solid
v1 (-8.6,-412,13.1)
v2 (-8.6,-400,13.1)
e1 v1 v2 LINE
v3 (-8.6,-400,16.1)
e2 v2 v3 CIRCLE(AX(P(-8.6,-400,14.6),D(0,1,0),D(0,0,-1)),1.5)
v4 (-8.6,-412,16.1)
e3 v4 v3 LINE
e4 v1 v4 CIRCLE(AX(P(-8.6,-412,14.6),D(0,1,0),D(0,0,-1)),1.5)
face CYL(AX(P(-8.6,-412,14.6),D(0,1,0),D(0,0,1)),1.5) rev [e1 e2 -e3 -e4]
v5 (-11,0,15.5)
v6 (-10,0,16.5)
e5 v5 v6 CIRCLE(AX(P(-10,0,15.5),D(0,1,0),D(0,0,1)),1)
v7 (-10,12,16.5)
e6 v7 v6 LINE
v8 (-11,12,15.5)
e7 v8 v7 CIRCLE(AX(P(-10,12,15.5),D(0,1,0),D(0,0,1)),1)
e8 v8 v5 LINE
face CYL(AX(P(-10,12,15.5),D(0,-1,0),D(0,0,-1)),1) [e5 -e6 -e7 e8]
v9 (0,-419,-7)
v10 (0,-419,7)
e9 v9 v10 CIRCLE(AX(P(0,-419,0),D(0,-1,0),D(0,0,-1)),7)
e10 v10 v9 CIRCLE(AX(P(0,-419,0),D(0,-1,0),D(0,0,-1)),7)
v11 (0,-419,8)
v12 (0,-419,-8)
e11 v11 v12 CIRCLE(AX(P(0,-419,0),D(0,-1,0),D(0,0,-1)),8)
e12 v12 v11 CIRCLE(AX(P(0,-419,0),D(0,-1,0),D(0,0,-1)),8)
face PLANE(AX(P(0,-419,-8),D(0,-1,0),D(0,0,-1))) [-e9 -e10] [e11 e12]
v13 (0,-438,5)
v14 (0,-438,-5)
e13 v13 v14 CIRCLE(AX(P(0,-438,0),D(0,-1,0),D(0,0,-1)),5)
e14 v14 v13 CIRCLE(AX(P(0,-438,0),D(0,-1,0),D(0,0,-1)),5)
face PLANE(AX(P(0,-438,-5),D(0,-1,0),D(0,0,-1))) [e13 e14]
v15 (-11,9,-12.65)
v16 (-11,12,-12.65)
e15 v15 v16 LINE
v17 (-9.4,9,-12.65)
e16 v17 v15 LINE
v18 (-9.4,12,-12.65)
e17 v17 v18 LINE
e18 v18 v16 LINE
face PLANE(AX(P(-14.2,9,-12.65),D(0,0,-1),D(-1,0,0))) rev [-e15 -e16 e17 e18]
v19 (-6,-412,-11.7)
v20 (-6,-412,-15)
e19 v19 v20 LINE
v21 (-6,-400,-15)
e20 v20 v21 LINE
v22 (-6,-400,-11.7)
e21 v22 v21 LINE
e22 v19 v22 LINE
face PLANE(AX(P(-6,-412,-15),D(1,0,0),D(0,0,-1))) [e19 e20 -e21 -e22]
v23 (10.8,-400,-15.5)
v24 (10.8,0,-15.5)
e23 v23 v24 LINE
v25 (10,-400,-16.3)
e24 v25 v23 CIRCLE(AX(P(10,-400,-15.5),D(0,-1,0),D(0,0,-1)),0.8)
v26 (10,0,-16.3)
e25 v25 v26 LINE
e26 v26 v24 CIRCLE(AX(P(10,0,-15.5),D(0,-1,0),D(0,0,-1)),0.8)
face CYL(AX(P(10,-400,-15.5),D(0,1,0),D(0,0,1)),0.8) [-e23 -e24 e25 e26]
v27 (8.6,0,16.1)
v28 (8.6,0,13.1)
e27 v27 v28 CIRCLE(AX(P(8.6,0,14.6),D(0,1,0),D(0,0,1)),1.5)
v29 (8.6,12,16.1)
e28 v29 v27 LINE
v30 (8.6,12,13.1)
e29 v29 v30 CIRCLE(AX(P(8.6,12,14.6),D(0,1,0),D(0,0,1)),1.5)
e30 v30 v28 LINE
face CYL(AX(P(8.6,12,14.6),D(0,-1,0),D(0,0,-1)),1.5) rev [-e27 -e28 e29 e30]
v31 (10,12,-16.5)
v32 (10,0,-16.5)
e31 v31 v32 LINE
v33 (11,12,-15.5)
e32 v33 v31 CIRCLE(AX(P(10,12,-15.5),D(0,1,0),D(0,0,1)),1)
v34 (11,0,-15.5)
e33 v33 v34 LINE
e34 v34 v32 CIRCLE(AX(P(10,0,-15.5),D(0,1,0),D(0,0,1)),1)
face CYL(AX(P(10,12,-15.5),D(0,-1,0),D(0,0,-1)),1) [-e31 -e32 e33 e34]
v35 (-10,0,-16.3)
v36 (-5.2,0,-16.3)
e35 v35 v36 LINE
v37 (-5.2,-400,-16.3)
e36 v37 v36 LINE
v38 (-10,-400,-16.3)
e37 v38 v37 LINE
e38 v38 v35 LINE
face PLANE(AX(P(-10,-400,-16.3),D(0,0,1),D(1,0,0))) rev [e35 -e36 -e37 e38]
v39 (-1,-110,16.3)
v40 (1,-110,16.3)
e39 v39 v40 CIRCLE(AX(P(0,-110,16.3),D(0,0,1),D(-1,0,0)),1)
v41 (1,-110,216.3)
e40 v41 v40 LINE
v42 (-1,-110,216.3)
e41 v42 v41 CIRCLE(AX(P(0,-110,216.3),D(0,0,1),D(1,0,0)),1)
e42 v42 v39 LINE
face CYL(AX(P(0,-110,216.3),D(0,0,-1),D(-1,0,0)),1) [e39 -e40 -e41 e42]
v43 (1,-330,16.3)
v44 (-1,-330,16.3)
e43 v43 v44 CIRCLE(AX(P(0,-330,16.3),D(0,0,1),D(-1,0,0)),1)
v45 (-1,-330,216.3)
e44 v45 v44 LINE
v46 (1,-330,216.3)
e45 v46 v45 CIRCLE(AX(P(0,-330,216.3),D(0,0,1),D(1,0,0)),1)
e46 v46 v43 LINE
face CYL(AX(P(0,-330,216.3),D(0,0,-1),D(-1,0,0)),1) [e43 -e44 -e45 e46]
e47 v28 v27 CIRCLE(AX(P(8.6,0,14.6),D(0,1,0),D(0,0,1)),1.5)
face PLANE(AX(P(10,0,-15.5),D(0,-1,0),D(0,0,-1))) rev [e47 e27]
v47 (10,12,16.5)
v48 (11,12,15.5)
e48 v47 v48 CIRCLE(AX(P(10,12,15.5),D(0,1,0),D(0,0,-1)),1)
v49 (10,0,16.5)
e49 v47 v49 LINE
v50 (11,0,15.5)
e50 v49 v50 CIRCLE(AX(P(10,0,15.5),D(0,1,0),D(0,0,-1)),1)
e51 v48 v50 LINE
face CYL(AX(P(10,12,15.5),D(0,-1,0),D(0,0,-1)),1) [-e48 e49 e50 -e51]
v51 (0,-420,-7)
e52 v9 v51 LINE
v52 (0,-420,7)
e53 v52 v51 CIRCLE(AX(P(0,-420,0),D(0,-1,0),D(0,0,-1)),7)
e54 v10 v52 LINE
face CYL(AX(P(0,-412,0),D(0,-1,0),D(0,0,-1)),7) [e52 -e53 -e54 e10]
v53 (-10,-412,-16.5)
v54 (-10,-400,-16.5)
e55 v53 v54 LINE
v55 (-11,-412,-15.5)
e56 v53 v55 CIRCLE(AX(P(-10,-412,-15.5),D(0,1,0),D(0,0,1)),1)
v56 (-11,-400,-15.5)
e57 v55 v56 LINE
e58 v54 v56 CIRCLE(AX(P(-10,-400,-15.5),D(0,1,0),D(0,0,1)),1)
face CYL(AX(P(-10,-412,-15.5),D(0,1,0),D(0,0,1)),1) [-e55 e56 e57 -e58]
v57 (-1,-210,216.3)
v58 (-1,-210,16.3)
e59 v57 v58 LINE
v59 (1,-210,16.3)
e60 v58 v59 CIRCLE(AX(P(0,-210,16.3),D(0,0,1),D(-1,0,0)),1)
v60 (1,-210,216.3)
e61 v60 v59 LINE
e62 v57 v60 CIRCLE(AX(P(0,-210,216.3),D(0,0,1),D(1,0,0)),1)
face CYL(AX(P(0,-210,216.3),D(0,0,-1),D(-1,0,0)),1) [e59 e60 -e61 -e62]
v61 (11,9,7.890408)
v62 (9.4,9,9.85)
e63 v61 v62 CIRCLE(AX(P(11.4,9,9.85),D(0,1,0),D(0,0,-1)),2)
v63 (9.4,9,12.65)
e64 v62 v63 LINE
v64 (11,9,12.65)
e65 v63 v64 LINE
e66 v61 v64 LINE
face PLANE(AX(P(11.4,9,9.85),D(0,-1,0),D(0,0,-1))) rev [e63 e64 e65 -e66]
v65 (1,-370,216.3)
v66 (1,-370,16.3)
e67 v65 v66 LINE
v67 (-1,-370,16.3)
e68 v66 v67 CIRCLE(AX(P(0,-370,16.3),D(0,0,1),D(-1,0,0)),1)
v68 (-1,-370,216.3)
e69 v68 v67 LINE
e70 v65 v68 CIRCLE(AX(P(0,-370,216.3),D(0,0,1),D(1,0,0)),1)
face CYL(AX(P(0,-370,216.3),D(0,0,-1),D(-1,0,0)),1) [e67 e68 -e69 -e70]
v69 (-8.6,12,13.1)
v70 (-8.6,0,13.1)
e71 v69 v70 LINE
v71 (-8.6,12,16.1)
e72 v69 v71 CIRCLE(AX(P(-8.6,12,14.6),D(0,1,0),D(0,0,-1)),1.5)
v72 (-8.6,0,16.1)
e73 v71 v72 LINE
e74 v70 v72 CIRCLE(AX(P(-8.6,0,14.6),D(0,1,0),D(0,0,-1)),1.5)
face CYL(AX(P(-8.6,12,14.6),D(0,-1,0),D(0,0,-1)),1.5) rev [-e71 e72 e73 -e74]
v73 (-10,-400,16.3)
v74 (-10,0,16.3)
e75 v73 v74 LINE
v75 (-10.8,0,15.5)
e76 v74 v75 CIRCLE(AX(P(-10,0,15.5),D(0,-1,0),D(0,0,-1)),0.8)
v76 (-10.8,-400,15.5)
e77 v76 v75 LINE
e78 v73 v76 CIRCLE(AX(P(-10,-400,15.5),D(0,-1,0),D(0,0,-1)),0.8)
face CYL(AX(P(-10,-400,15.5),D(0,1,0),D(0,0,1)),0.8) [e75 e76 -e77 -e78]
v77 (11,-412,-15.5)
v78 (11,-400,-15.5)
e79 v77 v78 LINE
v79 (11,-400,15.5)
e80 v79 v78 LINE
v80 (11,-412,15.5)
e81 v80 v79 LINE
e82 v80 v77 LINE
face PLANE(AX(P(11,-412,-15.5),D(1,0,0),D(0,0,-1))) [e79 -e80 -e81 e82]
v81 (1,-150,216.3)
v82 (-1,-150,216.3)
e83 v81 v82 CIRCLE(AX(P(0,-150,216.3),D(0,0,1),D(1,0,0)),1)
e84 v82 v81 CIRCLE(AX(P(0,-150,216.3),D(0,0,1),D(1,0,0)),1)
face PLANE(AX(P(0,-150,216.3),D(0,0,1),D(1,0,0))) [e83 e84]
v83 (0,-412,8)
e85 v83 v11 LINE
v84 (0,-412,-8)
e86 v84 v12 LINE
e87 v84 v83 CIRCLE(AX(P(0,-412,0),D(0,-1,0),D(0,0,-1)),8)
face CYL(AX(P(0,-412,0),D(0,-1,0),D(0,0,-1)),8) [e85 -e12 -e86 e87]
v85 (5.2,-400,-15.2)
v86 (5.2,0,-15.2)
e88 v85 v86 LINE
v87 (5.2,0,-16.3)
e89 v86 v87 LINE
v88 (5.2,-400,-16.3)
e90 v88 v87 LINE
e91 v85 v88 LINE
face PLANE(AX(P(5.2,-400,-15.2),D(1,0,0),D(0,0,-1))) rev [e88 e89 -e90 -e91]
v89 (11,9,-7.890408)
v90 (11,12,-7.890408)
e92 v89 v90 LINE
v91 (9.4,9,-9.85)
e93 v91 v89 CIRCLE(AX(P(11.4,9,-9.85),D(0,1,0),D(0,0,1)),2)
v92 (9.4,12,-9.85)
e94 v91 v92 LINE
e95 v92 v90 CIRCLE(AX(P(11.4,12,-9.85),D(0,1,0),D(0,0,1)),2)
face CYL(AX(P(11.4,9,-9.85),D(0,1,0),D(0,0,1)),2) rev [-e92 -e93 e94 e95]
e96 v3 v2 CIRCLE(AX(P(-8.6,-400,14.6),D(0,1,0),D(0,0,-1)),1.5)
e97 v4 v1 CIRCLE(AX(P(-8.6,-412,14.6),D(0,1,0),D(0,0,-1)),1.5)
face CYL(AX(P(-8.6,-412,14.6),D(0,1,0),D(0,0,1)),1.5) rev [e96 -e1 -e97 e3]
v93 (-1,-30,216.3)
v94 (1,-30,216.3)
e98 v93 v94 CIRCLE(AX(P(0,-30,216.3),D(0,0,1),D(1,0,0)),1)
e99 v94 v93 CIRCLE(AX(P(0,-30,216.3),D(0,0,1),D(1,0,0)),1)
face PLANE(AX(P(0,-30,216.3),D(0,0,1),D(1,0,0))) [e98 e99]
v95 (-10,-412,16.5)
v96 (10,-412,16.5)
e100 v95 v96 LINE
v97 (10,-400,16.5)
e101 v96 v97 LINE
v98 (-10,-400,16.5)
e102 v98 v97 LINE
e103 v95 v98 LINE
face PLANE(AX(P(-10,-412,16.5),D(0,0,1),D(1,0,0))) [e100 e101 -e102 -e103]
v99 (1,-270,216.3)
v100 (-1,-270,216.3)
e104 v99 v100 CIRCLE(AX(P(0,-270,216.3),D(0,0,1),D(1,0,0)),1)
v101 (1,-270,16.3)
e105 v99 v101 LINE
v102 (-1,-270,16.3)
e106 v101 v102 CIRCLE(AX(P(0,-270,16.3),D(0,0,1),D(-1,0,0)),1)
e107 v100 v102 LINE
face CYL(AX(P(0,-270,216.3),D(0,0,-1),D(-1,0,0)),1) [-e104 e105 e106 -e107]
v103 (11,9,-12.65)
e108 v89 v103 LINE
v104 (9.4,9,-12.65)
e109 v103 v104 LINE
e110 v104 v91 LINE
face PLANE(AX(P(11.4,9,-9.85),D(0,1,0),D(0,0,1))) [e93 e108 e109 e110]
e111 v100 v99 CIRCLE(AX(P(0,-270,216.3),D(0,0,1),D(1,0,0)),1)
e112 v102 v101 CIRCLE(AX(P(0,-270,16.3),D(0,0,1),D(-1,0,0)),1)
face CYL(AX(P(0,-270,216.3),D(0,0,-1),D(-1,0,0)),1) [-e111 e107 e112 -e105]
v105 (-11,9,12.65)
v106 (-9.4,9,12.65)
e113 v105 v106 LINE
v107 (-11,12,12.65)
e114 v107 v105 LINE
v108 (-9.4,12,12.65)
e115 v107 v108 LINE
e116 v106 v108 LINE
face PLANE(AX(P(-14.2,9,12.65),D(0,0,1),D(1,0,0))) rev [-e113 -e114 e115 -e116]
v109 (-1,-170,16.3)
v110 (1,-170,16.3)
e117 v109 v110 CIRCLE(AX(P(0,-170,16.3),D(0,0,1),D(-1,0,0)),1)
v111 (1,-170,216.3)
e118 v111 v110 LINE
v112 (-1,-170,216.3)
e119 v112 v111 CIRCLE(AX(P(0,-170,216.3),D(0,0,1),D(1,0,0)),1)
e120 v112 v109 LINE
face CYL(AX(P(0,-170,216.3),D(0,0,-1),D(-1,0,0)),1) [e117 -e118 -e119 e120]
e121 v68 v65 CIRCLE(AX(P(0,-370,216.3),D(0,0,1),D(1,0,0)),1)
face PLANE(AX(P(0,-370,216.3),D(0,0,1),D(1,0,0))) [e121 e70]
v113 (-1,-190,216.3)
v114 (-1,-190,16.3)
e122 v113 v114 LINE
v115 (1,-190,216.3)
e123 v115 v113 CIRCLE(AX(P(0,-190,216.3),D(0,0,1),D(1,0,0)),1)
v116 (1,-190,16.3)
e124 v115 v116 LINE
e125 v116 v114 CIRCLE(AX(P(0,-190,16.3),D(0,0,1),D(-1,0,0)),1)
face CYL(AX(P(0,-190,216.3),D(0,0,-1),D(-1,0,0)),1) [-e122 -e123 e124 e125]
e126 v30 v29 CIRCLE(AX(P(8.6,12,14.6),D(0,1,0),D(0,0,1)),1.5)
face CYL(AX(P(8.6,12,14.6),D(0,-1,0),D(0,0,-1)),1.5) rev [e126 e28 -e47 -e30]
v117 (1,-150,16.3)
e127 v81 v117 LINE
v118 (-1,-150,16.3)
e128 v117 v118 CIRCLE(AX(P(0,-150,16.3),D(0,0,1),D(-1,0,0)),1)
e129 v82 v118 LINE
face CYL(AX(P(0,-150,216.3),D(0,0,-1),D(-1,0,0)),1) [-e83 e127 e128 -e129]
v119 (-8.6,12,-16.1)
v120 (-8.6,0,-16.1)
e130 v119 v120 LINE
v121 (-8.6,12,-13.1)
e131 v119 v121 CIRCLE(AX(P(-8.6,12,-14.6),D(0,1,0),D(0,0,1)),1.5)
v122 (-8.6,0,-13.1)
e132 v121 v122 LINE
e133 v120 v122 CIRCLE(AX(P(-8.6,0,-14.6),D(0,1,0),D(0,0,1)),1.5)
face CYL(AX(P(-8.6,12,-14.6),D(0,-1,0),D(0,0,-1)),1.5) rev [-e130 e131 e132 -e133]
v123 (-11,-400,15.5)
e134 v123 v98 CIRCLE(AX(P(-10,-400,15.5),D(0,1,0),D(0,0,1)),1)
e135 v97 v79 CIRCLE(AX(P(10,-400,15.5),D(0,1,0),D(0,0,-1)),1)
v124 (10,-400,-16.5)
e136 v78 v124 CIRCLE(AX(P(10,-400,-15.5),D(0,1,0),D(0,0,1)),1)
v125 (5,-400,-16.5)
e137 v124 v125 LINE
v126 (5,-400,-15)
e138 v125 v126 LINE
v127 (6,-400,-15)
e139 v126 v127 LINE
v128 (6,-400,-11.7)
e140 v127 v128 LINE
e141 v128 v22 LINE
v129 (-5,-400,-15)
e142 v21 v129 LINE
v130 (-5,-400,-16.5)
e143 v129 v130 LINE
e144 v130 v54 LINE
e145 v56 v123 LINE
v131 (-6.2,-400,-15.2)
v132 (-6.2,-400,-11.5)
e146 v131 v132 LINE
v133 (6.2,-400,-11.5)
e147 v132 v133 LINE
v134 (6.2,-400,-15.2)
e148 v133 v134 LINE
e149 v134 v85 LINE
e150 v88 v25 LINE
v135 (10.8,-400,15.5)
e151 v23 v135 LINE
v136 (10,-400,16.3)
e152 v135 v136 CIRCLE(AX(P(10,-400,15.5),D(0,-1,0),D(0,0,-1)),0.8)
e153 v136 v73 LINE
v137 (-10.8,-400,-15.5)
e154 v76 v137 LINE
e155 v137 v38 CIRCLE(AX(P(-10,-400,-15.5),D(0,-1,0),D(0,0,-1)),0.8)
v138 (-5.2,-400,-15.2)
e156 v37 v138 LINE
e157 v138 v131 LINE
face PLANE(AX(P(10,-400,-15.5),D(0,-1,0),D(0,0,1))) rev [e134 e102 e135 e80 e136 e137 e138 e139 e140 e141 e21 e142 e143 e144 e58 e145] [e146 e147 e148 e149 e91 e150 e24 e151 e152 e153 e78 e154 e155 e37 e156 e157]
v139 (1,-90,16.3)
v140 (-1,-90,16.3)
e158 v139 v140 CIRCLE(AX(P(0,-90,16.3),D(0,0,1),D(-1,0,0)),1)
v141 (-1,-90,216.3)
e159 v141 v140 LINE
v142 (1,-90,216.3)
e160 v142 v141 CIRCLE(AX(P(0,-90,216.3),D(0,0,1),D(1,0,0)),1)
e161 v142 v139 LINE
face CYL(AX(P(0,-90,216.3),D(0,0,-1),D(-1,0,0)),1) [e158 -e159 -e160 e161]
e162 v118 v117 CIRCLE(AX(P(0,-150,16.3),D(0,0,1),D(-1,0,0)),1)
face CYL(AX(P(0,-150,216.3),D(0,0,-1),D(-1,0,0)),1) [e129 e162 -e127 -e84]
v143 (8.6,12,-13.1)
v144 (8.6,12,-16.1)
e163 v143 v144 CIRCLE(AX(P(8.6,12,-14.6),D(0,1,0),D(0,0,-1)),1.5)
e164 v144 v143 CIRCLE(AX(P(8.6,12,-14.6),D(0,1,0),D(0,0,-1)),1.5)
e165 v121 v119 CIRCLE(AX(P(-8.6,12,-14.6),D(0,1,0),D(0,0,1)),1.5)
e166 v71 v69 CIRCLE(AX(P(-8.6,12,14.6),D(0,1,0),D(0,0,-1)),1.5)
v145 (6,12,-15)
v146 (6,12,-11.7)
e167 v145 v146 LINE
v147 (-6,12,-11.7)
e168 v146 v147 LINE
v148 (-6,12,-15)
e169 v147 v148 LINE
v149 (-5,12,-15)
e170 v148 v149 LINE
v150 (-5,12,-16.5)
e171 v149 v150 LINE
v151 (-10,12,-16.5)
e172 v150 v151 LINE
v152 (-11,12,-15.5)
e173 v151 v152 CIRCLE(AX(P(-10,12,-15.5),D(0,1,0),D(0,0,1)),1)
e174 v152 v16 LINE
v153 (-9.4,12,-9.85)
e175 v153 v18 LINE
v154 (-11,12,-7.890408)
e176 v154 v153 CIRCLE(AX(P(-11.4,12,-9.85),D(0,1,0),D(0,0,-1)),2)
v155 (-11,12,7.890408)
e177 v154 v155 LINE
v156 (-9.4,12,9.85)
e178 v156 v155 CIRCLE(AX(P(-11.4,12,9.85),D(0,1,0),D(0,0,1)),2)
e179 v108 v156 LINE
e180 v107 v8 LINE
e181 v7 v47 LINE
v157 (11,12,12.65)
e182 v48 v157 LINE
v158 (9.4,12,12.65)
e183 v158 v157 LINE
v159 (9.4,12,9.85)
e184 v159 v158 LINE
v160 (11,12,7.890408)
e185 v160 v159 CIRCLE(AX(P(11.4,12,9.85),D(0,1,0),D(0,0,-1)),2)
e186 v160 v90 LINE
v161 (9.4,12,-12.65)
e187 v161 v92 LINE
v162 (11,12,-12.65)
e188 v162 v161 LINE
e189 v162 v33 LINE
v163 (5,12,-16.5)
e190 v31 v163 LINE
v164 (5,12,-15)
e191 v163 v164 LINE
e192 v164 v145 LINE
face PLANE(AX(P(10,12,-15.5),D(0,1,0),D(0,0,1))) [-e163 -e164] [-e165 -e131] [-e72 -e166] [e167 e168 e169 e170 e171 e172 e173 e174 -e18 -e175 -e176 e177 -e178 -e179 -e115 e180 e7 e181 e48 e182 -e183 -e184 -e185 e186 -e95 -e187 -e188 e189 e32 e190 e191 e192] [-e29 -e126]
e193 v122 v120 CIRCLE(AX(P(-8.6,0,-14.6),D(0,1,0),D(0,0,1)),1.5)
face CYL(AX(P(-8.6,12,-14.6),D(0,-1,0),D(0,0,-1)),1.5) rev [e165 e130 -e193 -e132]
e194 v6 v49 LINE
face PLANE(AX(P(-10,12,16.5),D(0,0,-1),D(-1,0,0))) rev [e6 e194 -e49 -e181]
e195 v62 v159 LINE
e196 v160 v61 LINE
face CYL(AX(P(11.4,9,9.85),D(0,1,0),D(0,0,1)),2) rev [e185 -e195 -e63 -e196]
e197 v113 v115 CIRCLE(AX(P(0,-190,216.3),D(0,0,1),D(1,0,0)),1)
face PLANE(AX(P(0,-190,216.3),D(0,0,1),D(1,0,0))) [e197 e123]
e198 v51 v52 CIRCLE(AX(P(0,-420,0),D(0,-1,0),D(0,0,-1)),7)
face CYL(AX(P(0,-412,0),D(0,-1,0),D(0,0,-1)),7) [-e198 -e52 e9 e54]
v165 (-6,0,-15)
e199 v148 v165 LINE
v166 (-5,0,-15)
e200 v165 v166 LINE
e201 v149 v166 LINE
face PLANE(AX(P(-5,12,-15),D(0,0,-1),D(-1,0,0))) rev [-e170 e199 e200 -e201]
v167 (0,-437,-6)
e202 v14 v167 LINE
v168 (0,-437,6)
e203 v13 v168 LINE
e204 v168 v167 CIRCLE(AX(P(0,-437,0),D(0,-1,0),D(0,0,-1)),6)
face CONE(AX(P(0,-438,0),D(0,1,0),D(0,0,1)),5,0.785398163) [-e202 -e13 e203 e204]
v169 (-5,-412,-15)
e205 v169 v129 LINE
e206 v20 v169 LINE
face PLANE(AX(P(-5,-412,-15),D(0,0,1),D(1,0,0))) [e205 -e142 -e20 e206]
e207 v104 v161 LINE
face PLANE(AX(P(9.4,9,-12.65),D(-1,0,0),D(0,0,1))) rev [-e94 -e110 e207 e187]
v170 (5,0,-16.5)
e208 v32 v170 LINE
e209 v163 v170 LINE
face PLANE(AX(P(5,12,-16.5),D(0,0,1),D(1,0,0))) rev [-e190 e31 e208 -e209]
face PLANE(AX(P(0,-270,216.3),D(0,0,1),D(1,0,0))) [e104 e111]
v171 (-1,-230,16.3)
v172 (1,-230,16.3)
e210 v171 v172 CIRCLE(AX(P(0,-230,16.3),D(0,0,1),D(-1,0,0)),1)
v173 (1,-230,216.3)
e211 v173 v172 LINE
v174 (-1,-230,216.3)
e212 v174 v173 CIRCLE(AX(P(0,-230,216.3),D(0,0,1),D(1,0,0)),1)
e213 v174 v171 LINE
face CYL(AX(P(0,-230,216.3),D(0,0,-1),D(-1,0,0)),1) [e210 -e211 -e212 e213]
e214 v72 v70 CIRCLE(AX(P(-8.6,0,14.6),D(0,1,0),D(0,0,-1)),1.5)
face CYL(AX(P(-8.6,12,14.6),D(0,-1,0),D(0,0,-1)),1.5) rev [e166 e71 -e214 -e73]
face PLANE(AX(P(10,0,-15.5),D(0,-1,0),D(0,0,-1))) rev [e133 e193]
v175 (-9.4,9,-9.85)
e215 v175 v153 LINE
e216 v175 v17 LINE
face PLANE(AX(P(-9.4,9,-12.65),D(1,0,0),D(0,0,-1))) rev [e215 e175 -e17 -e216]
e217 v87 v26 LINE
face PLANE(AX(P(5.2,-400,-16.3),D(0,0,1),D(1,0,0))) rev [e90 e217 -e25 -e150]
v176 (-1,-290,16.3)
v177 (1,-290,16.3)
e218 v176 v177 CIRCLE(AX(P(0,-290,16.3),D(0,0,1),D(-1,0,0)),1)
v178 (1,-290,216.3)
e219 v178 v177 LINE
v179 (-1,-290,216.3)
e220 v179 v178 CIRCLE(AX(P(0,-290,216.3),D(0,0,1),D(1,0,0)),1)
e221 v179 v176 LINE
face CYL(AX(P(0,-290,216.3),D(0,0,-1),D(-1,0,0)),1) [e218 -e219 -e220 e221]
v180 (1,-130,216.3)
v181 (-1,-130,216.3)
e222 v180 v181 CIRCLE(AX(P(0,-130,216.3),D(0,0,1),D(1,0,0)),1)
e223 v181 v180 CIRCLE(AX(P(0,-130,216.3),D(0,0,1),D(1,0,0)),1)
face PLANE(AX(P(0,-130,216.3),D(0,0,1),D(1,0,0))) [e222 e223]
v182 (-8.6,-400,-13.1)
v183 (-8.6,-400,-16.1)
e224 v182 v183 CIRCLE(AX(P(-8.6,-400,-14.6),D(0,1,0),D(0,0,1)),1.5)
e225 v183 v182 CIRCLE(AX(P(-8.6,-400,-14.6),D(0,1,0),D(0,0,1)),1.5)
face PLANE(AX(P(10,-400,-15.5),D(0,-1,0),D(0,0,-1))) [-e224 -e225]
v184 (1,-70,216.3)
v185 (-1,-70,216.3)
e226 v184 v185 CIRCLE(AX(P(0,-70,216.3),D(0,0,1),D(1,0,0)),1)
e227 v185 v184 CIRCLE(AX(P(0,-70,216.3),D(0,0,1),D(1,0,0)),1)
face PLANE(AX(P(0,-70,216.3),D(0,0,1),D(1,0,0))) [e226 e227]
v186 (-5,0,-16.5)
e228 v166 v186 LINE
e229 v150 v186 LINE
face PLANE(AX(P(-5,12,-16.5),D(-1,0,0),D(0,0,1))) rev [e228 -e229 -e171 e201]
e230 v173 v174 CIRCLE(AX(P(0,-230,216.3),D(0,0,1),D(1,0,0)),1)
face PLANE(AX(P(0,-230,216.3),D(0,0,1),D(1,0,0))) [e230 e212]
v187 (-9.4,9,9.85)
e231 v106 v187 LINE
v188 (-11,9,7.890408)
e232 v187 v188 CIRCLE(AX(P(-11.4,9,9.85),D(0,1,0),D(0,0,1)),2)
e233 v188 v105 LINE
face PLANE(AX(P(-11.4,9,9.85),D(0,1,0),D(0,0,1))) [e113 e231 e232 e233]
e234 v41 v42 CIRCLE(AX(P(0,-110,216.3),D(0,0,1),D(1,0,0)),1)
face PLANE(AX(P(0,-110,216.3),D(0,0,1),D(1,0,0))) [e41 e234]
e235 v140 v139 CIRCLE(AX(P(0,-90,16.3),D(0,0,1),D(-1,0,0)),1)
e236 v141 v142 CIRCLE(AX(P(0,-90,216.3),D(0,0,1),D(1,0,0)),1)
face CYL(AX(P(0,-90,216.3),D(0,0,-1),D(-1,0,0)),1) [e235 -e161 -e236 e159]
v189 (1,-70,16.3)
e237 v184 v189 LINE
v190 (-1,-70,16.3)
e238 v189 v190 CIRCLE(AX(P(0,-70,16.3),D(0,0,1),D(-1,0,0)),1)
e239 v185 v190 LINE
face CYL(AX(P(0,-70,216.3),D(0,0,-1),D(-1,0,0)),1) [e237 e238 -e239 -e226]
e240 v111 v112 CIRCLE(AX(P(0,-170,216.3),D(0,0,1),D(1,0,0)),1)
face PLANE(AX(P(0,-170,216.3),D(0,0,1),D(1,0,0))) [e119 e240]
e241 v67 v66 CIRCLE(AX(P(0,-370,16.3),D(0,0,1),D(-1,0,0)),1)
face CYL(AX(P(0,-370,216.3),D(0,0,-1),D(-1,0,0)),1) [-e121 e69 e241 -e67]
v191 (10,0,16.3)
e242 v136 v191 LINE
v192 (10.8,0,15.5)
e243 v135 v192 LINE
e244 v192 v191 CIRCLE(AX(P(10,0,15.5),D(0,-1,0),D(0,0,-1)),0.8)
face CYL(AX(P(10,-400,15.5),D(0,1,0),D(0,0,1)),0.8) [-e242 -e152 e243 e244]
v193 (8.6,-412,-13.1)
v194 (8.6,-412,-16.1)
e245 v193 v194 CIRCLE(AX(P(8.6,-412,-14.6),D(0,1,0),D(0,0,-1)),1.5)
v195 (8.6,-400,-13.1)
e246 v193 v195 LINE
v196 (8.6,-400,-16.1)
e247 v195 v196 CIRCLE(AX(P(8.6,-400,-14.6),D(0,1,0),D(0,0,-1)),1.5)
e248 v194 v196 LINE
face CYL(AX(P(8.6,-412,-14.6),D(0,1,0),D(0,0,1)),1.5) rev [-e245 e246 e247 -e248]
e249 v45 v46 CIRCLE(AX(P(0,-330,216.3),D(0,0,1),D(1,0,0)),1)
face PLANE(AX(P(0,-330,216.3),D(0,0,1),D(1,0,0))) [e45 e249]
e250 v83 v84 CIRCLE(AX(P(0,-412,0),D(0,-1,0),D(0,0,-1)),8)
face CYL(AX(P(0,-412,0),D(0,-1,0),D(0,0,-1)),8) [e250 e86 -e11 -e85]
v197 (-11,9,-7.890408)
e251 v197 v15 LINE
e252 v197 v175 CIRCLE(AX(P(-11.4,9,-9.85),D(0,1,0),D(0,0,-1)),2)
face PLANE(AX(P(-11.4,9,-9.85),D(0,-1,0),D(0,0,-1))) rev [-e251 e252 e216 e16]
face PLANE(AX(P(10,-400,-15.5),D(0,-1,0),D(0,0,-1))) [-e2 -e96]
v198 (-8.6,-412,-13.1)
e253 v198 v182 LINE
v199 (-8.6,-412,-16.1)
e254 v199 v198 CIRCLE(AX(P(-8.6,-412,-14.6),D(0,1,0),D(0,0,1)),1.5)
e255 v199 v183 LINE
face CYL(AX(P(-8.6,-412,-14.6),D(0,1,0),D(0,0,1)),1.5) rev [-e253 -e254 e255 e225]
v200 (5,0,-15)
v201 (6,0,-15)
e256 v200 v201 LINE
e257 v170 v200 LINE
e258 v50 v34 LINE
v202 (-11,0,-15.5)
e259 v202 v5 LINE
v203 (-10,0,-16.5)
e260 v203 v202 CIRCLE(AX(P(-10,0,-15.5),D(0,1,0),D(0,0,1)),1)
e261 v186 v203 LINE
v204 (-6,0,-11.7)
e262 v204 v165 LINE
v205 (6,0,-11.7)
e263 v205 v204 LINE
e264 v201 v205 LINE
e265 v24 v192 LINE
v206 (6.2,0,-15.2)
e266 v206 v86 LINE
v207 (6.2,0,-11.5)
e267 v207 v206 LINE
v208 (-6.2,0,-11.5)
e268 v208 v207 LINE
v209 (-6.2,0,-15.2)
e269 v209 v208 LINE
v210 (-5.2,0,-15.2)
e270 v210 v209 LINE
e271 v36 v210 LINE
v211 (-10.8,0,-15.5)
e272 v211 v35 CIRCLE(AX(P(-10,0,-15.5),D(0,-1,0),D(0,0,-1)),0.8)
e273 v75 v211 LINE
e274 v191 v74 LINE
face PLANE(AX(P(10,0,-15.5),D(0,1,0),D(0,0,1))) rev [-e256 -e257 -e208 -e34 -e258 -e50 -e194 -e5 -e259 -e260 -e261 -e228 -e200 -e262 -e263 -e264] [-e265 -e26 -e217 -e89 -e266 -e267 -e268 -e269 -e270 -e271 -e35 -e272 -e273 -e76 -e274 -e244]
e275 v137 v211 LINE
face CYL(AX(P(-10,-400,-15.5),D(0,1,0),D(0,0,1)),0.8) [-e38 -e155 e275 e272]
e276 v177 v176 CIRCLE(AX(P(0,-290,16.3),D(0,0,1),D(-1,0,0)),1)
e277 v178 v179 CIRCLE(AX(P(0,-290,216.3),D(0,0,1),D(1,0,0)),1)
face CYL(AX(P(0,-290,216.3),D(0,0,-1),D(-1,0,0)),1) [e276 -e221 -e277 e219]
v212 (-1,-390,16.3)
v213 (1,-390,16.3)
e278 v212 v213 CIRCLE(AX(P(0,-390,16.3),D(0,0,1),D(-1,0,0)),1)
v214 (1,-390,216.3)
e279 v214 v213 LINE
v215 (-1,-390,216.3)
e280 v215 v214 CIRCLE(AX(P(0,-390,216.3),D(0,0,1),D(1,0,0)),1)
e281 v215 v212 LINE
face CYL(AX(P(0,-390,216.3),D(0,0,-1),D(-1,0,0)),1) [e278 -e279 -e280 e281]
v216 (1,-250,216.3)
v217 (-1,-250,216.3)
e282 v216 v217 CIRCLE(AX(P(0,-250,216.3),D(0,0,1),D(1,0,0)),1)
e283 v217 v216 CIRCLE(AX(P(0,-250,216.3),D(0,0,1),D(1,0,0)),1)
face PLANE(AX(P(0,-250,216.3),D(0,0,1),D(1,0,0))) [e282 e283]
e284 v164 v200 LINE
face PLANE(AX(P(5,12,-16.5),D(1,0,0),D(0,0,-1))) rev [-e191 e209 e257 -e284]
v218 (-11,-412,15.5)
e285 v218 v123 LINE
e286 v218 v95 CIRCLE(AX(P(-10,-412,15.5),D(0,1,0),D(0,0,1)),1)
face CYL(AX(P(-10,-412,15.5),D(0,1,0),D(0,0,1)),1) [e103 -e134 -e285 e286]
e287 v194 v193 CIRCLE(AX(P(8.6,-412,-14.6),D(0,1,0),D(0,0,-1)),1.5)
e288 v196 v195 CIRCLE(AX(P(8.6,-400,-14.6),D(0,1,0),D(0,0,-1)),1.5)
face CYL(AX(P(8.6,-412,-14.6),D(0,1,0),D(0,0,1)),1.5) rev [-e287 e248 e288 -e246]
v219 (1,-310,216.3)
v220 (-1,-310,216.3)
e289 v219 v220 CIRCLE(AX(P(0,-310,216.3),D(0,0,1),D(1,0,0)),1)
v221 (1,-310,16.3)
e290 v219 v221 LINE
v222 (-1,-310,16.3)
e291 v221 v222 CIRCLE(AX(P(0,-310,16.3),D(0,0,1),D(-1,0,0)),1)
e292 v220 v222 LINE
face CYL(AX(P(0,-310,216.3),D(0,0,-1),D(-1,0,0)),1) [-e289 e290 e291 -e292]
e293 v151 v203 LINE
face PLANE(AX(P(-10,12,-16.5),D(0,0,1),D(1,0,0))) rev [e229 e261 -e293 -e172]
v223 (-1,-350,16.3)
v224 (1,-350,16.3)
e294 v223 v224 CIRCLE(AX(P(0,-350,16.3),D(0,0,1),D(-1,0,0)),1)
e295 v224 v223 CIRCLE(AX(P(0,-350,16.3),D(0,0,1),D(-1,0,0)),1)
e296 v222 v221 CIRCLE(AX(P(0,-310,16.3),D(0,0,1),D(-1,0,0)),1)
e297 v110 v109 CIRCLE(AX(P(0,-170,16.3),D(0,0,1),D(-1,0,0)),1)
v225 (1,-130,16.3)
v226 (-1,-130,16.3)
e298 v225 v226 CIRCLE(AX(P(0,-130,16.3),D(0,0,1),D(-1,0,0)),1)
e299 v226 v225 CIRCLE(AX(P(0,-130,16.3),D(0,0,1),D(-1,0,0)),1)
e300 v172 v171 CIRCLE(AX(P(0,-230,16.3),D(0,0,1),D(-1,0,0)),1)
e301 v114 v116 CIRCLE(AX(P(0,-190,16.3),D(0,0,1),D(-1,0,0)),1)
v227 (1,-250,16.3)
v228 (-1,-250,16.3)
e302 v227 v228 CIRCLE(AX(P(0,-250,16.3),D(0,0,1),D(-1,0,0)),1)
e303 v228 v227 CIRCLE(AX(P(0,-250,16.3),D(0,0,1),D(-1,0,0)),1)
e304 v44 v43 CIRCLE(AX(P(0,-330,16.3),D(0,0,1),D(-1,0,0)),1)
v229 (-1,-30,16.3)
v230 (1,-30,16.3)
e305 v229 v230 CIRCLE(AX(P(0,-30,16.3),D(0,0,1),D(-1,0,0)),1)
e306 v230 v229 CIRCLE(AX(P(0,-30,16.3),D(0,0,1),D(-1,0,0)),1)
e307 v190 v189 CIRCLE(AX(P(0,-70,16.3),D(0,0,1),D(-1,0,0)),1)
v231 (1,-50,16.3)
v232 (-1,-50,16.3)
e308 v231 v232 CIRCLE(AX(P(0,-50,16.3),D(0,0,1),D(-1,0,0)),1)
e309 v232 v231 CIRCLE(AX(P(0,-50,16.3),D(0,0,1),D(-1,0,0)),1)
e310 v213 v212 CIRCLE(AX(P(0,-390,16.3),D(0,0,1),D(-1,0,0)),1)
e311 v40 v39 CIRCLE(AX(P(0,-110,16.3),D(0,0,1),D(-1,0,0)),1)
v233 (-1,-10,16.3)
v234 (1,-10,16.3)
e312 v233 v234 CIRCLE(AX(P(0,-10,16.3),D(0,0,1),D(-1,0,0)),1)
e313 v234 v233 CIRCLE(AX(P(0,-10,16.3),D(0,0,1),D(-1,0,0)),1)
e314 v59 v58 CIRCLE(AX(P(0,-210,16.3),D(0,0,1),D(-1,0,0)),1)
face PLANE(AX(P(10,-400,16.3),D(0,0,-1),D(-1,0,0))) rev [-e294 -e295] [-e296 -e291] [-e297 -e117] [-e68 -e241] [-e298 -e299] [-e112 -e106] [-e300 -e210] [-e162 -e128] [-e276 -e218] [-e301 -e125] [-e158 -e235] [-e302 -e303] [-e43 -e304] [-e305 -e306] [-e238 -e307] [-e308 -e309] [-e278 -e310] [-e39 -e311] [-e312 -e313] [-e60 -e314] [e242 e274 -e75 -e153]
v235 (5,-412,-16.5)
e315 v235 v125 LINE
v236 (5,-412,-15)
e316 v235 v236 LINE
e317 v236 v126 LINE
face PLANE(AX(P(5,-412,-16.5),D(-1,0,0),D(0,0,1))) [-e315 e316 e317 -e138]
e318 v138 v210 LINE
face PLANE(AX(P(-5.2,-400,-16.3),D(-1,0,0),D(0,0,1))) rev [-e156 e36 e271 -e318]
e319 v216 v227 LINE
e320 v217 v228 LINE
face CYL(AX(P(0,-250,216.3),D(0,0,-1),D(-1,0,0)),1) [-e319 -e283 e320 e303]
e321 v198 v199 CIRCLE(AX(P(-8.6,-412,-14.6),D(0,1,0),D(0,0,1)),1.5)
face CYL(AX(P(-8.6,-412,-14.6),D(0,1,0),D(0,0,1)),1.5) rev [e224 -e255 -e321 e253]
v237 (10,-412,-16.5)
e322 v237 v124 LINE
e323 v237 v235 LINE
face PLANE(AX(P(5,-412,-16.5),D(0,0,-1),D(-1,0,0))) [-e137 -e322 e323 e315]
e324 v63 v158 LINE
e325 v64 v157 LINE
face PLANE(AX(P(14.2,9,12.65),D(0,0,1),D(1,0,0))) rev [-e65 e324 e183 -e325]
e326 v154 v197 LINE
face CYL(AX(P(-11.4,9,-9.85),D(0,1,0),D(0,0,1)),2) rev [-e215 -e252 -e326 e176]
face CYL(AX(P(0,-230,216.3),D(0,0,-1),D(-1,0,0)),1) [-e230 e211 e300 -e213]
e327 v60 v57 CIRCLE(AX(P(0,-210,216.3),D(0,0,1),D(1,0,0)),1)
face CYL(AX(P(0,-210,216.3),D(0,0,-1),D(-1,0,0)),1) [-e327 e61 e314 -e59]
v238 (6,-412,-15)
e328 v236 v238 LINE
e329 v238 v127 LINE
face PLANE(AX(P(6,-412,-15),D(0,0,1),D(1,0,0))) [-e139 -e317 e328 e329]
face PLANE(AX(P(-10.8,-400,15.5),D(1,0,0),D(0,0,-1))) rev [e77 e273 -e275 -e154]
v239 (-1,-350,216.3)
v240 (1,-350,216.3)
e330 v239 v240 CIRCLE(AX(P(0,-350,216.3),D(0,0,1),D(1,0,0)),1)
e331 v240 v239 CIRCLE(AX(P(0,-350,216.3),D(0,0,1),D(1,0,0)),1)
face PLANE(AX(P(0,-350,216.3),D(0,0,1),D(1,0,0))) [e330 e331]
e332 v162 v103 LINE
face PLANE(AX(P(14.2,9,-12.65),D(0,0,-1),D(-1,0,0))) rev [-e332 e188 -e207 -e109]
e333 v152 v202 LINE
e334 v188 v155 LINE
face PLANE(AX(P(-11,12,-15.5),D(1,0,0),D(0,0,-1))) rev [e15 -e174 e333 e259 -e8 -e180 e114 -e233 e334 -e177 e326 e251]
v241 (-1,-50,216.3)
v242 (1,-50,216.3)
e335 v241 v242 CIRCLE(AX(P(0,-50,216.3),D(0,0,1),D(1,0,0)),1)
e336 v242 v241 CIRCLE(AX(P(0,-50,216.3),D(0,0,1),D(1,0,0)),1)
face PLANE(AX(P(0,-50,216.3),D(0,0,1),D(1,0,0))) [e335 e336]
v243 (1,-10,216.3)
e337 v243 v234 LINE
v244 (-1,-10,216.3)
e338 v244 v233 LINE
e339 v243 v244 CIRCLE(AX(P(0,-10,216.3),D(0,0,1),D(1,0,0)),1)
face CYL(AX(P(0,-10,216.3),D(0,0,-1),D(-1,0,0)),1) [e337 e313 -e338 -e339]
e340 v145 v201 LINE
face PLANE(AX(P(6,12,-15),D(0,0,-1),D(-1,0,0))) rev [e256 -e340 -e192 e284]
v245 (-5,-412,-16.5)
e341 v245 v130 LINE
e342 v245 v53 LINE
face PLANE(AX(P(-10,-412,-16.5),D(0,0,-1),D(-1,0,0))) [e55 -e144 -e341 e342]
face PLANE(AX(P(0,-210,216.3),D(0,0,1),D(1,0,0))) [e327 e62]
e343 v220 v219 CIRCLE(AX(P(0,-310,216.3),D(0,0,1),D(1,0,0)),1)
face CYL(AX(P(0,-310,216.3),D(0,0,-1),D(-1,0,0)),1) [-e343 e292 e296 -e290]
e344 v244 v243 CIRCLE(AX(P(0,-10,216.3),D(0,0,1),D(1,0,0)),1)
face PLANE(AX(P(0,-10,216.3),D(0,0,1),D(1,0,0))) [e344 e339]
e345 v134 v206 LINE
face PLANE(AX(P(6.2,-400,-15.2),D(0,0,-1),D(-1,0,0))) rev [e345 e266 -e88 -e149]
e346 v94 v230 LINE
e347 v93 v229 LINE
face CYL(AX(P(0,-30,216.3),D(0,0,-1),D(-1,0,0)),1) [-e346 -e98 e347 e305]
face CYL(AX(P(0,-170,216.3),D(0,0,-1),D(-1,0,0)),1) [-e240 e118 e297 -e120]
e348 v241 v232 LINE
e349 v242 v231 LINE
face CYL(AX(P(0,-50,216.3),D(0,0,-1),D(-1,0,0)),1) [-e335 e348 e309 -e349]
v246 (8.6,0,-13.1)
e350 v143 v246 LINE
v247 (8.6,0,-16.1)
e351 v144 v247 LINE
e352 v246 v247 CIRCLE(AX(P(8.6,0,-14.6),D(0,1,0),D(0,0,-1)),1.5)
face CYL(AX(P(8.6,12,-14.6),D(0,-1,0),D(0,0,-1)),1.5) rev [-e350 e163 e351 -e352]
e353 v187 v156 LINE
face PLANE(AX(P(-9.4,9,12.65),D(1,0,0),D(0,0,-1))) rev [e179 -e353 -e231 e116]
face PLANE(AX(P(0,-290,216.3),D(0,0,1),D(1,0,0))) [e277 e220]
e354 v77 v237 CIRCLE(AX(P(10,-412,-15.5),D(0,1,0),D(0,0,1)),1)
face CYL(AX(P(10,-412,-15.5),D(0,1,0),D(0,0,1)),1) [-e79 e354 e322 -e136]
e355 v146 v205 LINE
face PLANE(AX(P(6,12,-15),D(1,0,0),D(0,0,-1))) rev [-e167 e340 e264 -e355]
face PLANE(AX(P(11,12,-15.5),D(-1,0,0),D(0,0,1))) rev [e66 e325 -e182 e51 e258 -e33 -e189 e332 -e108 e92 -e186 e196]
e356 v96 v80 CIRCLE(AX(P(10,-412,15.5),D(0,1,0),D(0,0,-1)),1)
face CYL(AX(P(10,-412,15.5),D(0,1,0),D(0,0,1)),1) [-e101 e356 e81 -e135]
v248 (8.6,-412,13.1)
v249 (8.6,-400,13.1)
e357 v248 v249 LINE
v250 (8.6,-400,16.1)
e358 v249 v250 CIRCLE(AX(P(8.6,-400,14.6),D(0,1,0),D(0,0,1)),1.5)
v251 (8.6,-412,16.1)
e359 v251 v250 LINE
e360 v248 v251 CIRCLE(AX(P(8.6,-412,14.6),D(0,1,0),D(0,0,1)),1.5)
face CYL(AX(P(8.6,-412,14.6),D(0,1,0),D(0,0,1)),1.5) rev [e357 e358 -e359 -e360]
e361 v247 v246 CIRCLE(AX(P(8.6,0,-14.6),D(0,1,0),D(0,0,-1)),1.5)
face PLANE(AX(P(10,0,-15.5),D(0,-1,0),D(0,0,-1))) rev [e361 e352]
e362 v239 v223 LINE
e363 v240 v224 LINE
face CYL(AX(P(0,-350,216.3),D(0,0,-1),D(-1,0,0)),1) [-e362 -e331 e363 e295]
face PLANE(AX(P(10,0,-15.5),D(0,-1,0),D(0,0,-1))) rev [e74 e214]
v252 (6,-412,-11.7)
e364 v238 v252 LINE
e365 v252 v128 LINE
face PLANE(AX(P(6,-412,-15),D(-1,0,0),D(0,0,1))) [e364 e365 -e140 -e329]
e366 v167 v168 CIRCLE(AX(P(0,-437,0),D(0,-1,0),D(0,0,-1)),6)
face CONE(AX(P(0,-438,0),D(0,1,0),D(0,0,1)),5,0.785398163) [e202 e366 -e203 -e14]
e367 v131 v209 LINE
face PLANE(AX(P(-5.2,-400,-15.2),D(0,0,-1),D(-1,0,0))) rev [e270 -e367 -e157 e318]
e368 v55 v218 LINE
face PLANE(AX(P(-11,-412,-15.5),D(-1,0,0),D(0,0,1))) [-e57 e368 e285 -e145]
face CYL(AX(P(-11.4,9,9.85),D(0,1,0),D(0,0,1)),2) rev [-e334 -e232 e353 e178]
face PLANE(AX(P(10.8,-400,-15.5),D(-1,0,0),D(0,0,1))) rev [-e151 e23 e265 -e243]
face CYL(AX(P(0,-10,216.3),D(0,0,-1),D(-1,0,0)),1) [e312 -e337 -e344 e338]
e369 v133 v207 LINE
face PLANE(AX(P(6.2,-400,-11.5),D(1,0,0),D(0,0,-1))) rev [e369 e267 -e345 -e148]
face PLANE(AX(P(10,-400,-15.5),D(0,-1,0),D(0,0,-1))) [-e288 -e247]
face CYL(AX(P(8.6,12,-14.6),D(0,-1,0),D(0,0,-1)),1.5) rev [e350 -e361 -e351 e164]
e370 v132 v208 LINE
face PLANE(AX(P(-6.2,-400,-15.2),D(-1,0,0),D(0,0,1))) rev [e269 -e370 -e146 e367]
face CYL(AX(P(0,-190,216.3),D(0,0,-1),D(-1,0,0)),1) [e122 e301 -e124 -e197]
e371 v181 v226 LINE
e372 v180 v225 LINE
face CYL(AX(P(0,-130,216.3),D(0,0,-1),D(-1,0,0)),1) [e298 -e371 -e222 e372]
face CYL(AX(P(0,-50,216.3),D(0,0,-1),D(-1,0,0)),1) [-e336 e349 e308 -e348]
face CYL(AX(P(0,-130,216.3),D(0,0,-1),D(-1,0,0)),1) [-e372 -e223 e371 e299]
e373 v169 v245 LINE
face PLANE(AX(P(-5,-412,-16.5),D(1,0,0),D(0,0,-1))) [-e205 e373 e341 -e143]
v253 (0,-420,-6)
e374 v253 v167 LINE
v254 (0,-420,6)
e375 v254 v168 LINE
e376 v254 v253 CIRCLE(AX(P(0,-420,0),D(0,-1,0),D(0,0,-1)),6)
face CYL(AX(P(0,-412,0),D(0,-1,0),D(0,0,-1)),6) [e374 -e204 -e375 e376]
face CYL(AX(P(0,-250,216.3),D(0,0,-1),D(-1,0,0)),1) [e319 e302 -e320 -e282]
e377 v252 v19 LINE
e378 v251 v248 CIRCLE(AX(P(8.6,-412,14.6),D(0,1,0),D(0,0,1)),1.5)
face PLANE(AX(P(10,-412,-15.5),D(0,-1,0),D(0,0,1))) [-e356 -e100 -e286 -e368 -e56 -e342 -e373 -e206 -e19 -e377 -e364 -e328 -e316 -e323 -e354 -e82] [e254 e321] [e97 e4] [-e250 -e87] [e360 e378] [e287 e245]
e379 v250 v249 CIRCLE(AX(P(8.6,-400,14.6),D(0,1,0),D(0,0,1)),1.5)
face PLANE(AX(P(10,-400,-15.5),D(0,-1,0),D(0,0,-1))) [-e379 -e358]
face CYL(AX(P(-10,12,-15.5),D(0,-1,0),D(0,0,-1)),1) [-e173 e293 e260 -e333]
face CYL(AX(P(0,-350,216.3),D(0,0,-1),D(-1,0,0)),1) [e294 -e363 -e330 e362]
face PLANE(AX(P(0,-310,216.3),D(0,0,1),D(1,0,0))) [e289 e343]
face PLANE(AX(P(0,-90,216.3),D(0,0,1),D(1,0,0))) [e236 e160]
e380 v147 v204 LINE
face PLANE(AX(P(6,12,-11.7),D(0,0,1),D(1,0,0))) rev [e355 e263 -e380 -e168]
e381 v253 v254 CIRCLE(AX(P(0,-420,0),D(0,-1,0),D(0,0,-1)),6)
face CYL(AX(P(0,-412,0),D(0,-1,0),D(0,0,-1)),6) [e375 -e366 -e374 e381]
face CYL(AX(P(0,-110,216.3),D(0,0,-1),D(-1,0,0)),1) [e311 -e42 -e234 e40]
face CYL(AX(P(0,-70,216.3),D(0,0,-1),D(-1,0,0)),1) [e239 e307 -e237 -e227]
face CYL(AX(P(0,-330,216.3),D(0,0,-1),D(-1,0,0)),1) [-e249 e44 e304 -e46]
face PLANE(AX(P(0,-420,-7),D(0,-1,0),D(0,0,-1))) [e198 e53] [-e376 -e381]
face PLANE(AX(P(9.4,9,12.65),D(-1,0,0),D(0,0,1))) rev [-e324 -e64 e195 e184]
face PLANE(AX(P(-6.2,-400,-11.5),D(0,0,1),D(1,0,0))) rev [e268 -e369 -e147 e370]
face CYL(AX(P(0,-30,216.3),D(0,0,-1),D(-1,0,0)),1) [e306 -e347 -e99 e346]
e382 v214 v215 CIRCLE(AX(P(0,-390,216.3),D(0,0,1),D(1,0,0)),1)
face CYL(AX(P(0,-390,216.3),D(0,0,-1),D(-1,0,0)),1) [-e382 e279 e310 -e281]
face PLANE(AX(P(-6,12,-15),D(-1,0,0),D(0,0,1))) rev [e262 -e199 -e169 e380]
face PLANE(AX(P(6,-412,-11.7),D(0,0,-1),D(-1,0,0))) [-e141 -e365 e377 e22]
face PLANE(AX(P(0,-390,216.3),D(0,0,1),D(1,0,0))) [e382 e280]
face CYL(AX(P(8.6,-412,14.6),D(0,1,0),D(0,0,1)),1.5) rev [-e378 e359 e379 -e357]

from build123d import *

# Parameters (mm, degrees)
SKETCH_1_R             = 1.5
EXTRUDE_1_DEPTH        = 12
CUT_EXTRUDE_2_DEPTH    = 3
EXTRUDE_3_DEPTH        = 400
SKETCH_5_R             = 1
EXTRUDE_4_DEPTH        = 200
PATTERN_LINEAR_1_COUNT = 20
PATTERN_LINEAR_1_PITCH = 20


with BuildPart() as part:
    # 草圖1 → 伸長1 (new body)
    with BuildSketch(Plane(origin=(0, 0, 0), x_dir=(1, 0, 0), z_dir=(0, 1, 0))):
        with BuildLine():
            Line((-10, 16.5), (-5, 16.5))
            Line((-5, 16.5), (-5, 15))
            Line((-5, 15), (-6, 15))
            Line((-6, 15), (-6, 11.7))
            Line((-6, 11.7), (6, 11.7))
            Line((6, 11.7), (6, 15))
            Line((6, 15), (5, 15))
            Line((5, 15), (5, 16.5))
            Line((5, 16.5), (10, 16.5))
            ThreePointArc((10, 16.5), (10.707106781, 16.207106781), (11, 15.5))
            Line((11, 15.5), (11, -15.5))
            ThreePointArc((11, -15.5), (10.707106781, -16.207106781), (10, -16.5))
            Line((10, -16.5), (-10, -16.5))
            ThreePointArc((-10, -16.5), (-10.707106781, -16.207106781), (-11, -15.5))
            Line((-11, -15.5), (-11, 15.5))
            ThreePointArc((-11, 15.5), (-10.707106781, 16.207106781), (-10, 16.5))
        make_face()
        with Locations(Location((-8.6, 14.6, 0), (0, 0, 270))):
            Circle(SKETCH_1_R, mode=Mode.SUBTRACT)
        with Locations(Location((8.6, 14.6, 0), (0, 0, 90))):
            Circle(SKETCH_1_R, mode=Mode.SUBTRACT)
        with Locations(Location((8.6, -14.6, 0), (0, 0, 270))):
            Circle(SKETCH_1_R, mode=Mode.SUBTRACT)
        with Locations(Location((-8.6, -14.6, 0), (0, 0, 90))):
            Circle(SKETCH_1_R, mode=Mode.SUBTRACT)
    extrude_1 = extrude(amount=EXTRUDE_1_DEPTH)

    # 草圖2 → 伸長2 (cut)
    with BuildSketch(Plane(origin=(0, 12, 0), x_dir=(1, 0, 0), z_dir=(0, 1, 0))):
        with BuildLine():
            Line((-14.2, 12.65), (-9.4, 12.65))
            Line((-9.4, 12.65), (-9.4, 9.85))
            ThreePointArc((-9.4, 9.85), (-9.985786438, 8.435786438), (-11.4, 7.85))
            Line((-11.4, 7.85), (-14.2, 7.85))
            Line((-14.2, 7.85), (-14.2, 12.65))
        make_face()
        with BuildLine():
            Line((9.4, 12.65), (9.4, 9.85))
            ThreePointArc((9.4, 9.85), (9.985786438, 8.435786438), (11.4, 7.85))
            Line((11.4, 7.85), (14.2, 7.85))
            Line((14.2, 7.85), (14.2, 12.65))
            Line((14.2, 12.65), (9.4, 12.65))
        make_face()
        with BuildLine():
            Line((14.2, -12.65), (9.4, -12.65))
            Line((9.4, -12.65), (9.4, -9.85))
            ThreePointArc((9.4, -9.85), (9.985786438, -8.435786438), (11.4, -7.85))
            Line((11.4, -7.85), (14.2, -7.85))
            Line((14.2, -7.85), (14.2, -12.65))
        make_face()
        with BuildLine():
            Line((-9.4, -12.65), (-9.4, -9.85))
            ThreePointArc((-9.4, -9.85), (-9.985786438, -8.435786438), (-11.4, -7.85))
            Line((-11.4, -7.85), (-14.2, -7.85))
            Line((-14.2, -7.85), (-14.2, -12.65))
            Line((-14.2, -12.65), (-9.4, -12.65))
        make_face()
    extrude(amount=-CUT_EXTRUDE_2_DEPTH, mode=Mode.SUBTRACT)

    # 草圖3 → 伸長3 (add)
    with BuildSketch(Plane.XZ):
        with BuildLine():
            Line((-5.2, -16.3), (-5.2, -15.2))
            Line((-5.2, -15.2), (-6.2, -15.2))
            Line((-6.2, -15.2), (-6.2, -11.5))
            Line((-6.2, -11.5), (6.2, -11.5))
            Line((6.2, -11.5), (6.2, -15.2))
            Line((6.2, -15.2), (5.2, -15.2))
            Line((5.2, -15.2), (5.2, -16.3))
            Line((5.2, -16.3), (10, -16.3))
            ThreePointArc((10, -16.3), (10.565685425, -16.065685425), (10.8, -15.5))
            Line((10.8, -15.5), (10.8, 15.5))
            ThreePointArc((10.8, 15.5), (10.565685425, 16.065685425), (10, 16.3))
            Line((10, 16.3), (-10, 16.3))
            ThreePointArc((-10, 16.3), (-10.565685425, 16.065685425), (-10.8, 15.5))
            Line((-10.8, 15.5), (-10.8, -15.5))
            ThreePointArc((-10.8, -15.5), (-10.565685425, -16.065685425), (-10, -16.3))
            Line((-10, -16.3), (-5.2, -16.3))
        make_face()
    extrude(amount=EXTRUDE_3_DEPTH)

    # 鏡射1: 伸長1 across plane
    add(extrude_1.mirror(Plane.ZX.offset(-200)))

    # 草圖4 → 旋轉1 (revolve)
    with BuildSketch(Plane(origin=(0, 0, 0), x_dir=(0, 0, -1), z_dir=(1, 0, 0))):
        Polygon((8, -412), (8, -419), (7, -419), (7, -420), (6, -420), (6, -437), (5, -438), (0, -438), (0, -412), align=None)
    revolve(axis=Axis((0, -412, 0), (0, 1, 0)))

    # 草圖5 → 伸長4 (add)
    with BuildSketch(Plane.XY.offset(16.3)):
        with Locations(Location((0, -10, 0), (0, 0, 180))):
            Circle(SKETCH_5_R)
    extrude_4 = extrude(amount=EXTRUDE_4_DEPTH)

    # 阵列(线性)1: 伸長4 ×20
    with Locations(*[(0, -i * PATTERN_LINEAR_1_PITCH, 0) for i in range(1, PATTERN_LINEAR_1_COUNT)]):
        add(extrude_4)


solid = part.part
